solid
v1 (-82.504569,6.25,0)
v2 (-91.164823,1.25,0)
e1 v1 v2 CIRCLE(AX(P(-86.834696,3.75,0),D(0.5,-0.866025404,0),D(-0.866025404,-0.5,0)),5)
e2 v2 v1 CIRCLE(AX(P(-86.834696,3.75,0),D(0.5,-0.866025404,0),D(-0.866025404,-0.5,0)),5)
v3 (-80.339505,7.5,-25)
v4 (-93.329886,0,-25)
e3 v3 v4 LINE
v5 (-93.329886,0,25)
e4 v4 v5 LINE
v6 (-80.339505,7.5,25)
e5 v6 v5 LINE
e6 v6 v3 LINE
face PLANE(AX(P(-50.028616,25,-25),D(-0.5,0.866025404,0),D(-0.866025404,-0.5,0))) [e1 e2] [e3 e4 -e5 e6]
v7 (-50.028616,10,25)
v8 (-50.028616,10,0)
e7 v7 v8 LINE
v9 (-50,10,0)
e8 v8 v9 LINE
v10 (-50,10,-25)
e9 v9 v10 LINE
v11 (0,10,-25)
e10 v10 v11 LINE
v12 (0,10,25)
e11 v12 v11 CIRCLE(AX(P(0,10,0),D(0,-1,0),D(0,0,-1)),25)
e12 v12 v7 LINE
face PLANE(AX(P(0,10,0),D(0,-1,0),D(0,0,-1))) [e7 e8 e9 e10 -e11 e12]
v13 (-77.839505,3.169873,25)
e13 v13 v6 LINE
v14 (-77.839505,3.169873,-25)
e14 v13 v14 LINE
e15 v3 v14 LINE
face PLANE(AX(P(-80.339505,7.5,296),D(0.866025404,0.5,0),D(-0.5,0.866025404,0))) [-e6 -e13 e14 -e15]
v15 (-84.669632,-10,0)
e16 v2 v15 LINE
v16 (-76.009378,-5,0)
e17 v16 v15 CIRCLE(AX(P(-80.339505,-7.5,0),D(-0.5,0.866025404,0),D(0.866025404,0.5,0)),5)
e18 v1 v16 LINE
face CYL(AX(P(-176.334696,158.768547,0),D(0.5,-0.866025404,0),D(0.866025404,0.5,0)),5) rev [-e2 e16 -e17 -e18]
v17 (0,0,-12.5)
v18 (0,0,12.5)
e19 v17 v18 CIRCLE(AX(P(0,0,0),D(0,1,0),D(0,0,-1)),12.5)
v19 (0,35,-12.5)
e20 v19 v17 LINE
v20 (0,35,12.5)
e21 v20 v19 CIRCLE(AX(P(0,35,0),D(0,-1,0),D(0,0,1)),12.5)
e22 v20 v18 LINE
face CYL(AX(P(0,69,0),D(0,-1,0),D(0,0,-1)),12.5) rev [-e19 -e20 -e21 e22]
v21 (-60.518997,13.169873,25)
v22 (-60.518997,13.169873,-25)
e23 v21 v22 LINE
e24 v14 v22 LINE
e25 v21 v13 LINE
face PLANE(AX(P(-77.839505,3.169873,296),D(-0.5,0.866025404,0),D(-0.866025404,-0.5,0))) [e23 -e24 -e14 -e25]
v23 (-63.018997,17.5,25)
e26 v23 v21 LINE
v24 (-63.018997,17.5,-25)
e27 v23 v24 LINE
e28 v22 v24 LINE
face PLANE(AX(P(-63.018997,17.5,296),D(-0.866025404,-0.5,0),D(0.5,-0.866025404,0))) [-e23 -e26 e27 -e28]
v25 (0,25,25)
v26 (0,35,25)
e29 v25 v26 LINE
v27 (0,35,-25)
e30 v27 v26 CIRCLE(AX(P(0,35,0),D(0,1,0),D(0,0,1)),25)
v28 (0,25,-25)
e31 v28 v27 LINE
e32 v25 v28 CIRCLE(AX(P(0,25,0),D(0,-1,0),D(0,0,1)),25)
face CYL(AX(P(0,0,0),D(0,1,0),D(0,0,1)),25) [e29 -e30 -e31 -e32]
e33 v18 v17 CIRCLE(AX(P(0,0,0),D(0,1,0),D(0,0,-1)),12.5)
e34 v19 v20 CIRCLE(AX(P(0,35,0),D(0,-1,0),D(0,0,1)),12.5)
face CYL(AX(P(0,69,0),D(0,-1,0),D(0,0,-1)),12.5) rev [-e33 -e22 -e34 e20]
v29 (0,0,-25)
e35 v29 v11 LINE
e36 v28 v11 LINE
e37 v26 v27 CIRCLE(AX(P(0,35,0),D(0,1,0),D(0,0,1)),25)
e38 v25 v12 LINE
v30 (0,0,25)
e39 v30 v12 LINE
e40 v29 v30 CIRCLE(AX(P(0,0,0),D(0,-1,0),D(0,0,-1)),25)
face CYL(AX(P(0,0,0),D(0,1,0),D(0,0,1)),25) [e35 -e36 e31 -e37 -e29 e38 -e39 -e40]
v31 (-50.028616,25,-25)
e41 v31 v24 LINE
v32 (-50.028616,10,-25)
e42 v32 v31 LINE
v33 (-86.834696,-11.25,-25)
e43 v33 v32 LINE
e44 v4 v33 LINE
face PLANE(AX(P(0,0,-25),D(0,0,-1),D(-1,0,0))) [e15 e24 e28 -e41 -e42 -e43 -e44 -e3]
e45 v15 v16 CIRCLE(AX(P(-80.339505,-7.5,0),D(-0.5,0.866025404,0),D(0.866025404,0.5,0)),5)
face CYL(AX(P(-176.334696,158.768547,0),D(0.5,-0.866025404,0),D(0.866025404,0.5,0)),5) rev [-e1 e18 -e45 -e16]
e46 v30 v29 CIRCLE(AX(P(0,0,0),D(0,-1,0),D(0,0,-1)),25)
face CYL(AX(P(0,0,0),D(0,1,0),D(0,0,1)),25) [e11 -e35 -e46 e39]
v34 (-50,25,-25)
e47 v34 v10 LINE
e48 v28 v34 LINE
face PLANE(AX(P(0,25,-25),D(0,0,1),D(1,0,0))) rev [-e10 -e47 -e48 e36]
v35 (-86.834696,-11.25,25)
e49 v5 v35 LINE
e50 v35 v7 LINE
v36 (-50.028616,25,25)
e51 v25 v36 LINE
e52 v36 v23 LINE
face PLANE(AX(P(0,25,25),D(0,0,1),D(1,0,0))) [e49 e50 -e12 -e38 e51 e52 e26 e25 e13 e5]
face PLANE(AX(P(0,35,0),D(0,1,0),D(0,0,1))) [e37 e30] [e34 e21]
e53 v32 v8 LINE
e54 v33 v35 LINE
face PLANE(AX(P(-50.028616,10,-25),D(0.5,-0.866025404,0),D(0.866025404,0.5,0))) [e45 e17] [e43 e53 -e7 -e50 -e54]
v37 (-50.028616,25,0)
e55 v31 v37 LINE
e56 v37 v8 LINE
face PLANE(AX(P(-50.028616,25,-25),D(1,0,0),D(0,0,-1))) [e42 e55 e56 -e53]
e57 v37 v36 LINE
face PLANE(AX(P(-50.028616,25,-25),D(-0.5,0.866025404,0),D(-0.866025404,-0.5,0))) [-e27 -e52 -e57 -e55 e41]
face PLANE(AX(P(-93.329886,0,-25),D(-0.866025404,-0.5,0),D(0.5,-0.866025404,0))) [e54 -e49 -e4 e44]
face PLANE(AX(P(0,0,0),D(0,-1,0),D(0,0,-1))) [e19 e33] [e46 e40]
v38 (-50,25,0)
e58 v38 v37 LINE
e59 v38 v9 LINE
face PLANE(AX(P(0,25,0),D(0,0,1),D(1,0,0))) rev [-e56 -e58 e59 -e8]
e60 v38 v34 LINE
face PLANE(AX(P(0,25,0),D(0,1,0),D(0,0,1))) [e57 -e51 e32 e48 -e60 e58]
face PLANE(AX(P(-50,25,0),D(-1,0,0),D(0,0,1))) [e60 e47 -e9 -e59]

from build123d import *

# Parameters (mm, degrees)
HUB_BASE_25_SKETCH_R       = 12.5
HUB_BASE_25_DEPTH          = 10
HUB_SECTION_1_50_SKETCH_R  = 25
HUB_SECTION_1_50_DEPTH     = 10
HUB_NECK_1_25_SKETCH_R     = 12.5
HUB_NECK_1_25_DEPTH        = 15
HUB_SECTION_2_50_SKETCH_R  = 25
HUB_SECTION_2_50_DEPTH     = 15
HUB_NECK_2_25_SKETCH_R     = 12.5
HUB_NECK_2_25_DEPTH        = 10
HUB_TOP_50_SKETCH_R        = 25
HUB_TOP_50_DEPTH           = 10
ARM_BLOCK_SKETCH_W         = 25
ARM_BLOCK_SKETCH_H         = 15
ARM_BLOCK_DEPTH            = 25
ARM_WEB_PROFILE_SKETCH_W   = 50
ARM_WEB_PROFILE_SKETCH_H   = 25
ARM_WEB_PROFILE_SKETCH_W_2 = 50.02861625
ARM_WEB_DEPTH              = 25
ARM_START                  = -10
ARM_NOTCH_CUT_DEPTH        = 10
NOTCH_FILLER_SKETCH_R      = 25
NOTCH_FILLER_BOSS_DEPTH    = 10
HUB_BORE_25_DEPTH          = 34
HUB_BORE_25_DEPTH_BACK     = 80
HUB_BORE_25_SKETCH_R       = 12.5
DOVETAIL_RAIL_DEPTH        = 50
RAIL_GROOVE_CUT_DEPTH      = 271
RAIL_GROOVE_CUT_DEPTH_BACK = 142
RAIL_HOLE_10_DEPTH         = 179
RAIL_HOLE_10_DEPTH_BACK    = 179
RAIL_HOLE_10_SKETCH_R      = 5


with BuildPart() as part:
    # Hub Base _25 Sketch → Hub Base _25 (new body)
    with BuildSketch(Plane(origin=(0, 0, 0), x_dir=(1, 0, 0), z_dir=(0, 1, 0))):
        with Locations(Location((0, 0, 0), (0, 0, 270))):
            Circle(HUB_BASE_25_SKETCH_R)
    extrude(amount=HUB_BASE_25_DEPTH)

    # Hub Section 1 _50 Sketch → Hub Section 1 _50 (add)
    with BuildSketch(Plane(origin=(0, 10, 0), x_dir=(1, 0, 0), z_dir=(0, 1, 0))):
        with Locations(Location((0, 0, 0), (0, 0, 270))):
            Circle(HUB_SECTION_1_50_SKETCH_R)
    extrude(amount=-HUB_SECTION_1_50_DEPTH)

    # Hub Neck 1 _25 Sketch → Hub Neck 1 _25 (add)
    with BuildSketch(Plane(origin=(0, 10, 0), x_dir=(1, 0, 0), z_dir=(0, 1, 0))):
        with Locations(Location((0, 0, 0), (0, 0, 270))):
            Circle(HUB_NECK_1_25_SKETCH_R)
    extrude(amount=HUB_NECK_1_25_DEPTH)

    # Hub Section 2 _50 Sketch → Hub Section 2 _50 (add)
    with BuildSketch(Plane(origin=(0, 25, 0), x_dir=(1, 0, 0), z_dir=(0, 1, 0))):
        with Locations(Location((0, 0, 0), (0, 0, 270))):
            Circle(HUB_SECTION_2_50_SKETCH_R)
    extrude(amount=-HUB_SECTION_2_50_DEPTH)

    # Hub Neck 2 _25 Sketch → Hub Neck 2 _25 (add)
    with BuildSketch(Plane(origin=(0, 25, 0), x_dir=(1, 0, 0), z_dir=(0, 1, 0))):
        with Locations(Location((0, 0, 0), (0, 0, 270))):
            Circle(HUB_NECK_2_25_SKETCH_R)
    extrude(amount=HUB_NECK_2_25_DEPTH)

    # Hub Top _50 Sketch → Hub Top _50 (add)
    with BuildSketch(Plane(origin=(0, 35, 0), x_dir=(1, 0, 0), z_dir=(0, 1, 0))):
        with Locations(Location((0, 0, 0), (0, 0, 270))):
            Circle(HUB_TOP_50_SKETCH_R)
    extrude(amount=-HUB_TOP_50_DEPTH)



with BuildPart() as body_2:
    # Arm Block Sketch → Arm Block (new, symmetric)
    with BuildSketch(Plane.XY):
        with Locations((-37.5, 17.5)):
            Rectangle(ARM_BLOCK_SKETCH_W, ARM_BLOCK_SKETCH_H)
    extrude(amount=ARM_BLOCK_DEPTH, both=True)


with BuildPart() as part_1:
    add(part.part)

    add(body_2.part)  # Arm Web merges body 2
    # Arm Web Profile Sketch → Arm Web (add)
    with BuildSketch(Plane(origin=(0, 0, 0), x_dir=(1, 0, 0), z_dir=(0, 1, 0))):
        with Locations((-25, 12.5)):
            Rectangle(ARM_WEB_PROFILE_SKETCH_W, ARM_WEB_PROFILE_SKETCH_H)
        with Locations((-25.014308125, -12.5)):
            Rectangle(ARM_WEB_PROFILE_SKETCH_W_2, ARM_WEB_PROFILE_SKETCH_H)
    extrude(amount=ARM_WEB_DEPTH)

    # Arm Notch Sketch → Arm Notch Cut (cut)
    with BuildSketch(Plane.XZ.offset(ARM_START)):
        with BuildLine():
            Line((-2.42391296, 25), (-50.02861625, 25))
            Line((-50.02861625, 25), (-50.02861625, 0))
            Line((-50.02861625, 0), (-50, 0))
            Line((-50, 0), (-50, -25))
            Line((-50, -25), (-2.42391296, -25))
            ThreePointArc((-2.42391296, -25), (-25.117232213, 0), (-2.42391296, 25))
        make_face()
        with BuildLine():
            Line((0, 25), (-2.42391296, 25))
            ThreePointArc((-2.42391296, 25), (-25.117232213, 0), (-2.42391296, -25))
            Line((-2.42391296, -25), (0, -25))
            Line((0, -25), (0, 25))
        make_face()
        with BuildLine():
            Line((0, 25), (0, -25))
            ThreePointArc((0, -25), (25, 0), (0, 25))
        make_face()
    extrude(amount=ARM_NOTCH_CUT_DEPTH, mode=Mode.SUBTRACT)

    # Notch Filler Sketch → Notch Filler Boss (add)
    with BuildSketch(Plane.XZ.offset(-10)):
        with Locations(Location((0, 0, 0), (0, 0, 90))):
            Circle(NOTCH_FILLER_SKETCH_R)
    extrude(amount=NOTCH_FILLER_BOSS_DEPTH)

    # Hub Bore _25 Sketch → Hub Bore _25 (cut, two sides: drawn at the far end of the back side and taken through both)
    with BuildSketch(Plane(origin=(0, 35, 0), x_dir=(1, 0, 0), z_dir=(0, 1, 0)).offset(-HUB_BORE_25_DEPTH_BACK)):
        with Locations(Location((0, 0, 0), (0, 0, 90))):
            Circle(HUB_BORE_25_SKETCH_R)
    extrude(amount=HUB_BORE_25_DEPTH + HUB_BORE_25_DEPTH_BACK, mode=Mode.SUBTRACT)

    # Dovetail Rail Sketch → Dovetail Rail (add)
    with BuildSketch(Plane.XY.offset(25)):
        Polygon((-50.02861625, 10), (-86.834695911, -11.25), (-93.329886439, 0), (-50.02861625, 25), align=None)
    extrude(amount=-DOVETAIL_RAIL_DEPTH)

    # Rail Groove Sketch → Rail Groove Cut (cut, two sides: drawn at the far end of the back side and taken through both)
    with BuildSketch(Plane.XY.offset(25).offset(-RAIL_GROOVE_CUT_DEPTH_BACK)):
        Polygon((-80.339505382, 7.5), (-77.839505382, 3.169872981), (-60.518997307, 13.169872981), (-63.018997307, 17.5), align=None)
    extrude(amount=RAIL_GROOVE_CUT_DEPTH + RAIL_GROOVE_CUT_DEPTH_BACK, mode=Mode.SUBTRACT)

    # Rail Hole _10 Sketch → Rail Hole _10 (cut, two sides: drawn at the far end of the back side and taken through both)
    with BuildSketch(Plane(origin=(-23.33247161, 40.413026294, 0), x_dir=(0.8660254037844379, 0.5000000000000013, 0), z_dir=(-0.5000000000000013, 0.8660254037844379, 0)).offset(-RAIL_HOLE_10_DEPTH_BACK)):
        with Locations((-73.326052589, 0)):
            Circle(RAIL_HOLE_10_SKETCH_R)
    extrude(amount=RAIL_HOLE_10_DEPTH + RAIL_HOLE_10_DEPTH_BACK, mode=Mode.SUBTRACT)


solid = part_1.part
